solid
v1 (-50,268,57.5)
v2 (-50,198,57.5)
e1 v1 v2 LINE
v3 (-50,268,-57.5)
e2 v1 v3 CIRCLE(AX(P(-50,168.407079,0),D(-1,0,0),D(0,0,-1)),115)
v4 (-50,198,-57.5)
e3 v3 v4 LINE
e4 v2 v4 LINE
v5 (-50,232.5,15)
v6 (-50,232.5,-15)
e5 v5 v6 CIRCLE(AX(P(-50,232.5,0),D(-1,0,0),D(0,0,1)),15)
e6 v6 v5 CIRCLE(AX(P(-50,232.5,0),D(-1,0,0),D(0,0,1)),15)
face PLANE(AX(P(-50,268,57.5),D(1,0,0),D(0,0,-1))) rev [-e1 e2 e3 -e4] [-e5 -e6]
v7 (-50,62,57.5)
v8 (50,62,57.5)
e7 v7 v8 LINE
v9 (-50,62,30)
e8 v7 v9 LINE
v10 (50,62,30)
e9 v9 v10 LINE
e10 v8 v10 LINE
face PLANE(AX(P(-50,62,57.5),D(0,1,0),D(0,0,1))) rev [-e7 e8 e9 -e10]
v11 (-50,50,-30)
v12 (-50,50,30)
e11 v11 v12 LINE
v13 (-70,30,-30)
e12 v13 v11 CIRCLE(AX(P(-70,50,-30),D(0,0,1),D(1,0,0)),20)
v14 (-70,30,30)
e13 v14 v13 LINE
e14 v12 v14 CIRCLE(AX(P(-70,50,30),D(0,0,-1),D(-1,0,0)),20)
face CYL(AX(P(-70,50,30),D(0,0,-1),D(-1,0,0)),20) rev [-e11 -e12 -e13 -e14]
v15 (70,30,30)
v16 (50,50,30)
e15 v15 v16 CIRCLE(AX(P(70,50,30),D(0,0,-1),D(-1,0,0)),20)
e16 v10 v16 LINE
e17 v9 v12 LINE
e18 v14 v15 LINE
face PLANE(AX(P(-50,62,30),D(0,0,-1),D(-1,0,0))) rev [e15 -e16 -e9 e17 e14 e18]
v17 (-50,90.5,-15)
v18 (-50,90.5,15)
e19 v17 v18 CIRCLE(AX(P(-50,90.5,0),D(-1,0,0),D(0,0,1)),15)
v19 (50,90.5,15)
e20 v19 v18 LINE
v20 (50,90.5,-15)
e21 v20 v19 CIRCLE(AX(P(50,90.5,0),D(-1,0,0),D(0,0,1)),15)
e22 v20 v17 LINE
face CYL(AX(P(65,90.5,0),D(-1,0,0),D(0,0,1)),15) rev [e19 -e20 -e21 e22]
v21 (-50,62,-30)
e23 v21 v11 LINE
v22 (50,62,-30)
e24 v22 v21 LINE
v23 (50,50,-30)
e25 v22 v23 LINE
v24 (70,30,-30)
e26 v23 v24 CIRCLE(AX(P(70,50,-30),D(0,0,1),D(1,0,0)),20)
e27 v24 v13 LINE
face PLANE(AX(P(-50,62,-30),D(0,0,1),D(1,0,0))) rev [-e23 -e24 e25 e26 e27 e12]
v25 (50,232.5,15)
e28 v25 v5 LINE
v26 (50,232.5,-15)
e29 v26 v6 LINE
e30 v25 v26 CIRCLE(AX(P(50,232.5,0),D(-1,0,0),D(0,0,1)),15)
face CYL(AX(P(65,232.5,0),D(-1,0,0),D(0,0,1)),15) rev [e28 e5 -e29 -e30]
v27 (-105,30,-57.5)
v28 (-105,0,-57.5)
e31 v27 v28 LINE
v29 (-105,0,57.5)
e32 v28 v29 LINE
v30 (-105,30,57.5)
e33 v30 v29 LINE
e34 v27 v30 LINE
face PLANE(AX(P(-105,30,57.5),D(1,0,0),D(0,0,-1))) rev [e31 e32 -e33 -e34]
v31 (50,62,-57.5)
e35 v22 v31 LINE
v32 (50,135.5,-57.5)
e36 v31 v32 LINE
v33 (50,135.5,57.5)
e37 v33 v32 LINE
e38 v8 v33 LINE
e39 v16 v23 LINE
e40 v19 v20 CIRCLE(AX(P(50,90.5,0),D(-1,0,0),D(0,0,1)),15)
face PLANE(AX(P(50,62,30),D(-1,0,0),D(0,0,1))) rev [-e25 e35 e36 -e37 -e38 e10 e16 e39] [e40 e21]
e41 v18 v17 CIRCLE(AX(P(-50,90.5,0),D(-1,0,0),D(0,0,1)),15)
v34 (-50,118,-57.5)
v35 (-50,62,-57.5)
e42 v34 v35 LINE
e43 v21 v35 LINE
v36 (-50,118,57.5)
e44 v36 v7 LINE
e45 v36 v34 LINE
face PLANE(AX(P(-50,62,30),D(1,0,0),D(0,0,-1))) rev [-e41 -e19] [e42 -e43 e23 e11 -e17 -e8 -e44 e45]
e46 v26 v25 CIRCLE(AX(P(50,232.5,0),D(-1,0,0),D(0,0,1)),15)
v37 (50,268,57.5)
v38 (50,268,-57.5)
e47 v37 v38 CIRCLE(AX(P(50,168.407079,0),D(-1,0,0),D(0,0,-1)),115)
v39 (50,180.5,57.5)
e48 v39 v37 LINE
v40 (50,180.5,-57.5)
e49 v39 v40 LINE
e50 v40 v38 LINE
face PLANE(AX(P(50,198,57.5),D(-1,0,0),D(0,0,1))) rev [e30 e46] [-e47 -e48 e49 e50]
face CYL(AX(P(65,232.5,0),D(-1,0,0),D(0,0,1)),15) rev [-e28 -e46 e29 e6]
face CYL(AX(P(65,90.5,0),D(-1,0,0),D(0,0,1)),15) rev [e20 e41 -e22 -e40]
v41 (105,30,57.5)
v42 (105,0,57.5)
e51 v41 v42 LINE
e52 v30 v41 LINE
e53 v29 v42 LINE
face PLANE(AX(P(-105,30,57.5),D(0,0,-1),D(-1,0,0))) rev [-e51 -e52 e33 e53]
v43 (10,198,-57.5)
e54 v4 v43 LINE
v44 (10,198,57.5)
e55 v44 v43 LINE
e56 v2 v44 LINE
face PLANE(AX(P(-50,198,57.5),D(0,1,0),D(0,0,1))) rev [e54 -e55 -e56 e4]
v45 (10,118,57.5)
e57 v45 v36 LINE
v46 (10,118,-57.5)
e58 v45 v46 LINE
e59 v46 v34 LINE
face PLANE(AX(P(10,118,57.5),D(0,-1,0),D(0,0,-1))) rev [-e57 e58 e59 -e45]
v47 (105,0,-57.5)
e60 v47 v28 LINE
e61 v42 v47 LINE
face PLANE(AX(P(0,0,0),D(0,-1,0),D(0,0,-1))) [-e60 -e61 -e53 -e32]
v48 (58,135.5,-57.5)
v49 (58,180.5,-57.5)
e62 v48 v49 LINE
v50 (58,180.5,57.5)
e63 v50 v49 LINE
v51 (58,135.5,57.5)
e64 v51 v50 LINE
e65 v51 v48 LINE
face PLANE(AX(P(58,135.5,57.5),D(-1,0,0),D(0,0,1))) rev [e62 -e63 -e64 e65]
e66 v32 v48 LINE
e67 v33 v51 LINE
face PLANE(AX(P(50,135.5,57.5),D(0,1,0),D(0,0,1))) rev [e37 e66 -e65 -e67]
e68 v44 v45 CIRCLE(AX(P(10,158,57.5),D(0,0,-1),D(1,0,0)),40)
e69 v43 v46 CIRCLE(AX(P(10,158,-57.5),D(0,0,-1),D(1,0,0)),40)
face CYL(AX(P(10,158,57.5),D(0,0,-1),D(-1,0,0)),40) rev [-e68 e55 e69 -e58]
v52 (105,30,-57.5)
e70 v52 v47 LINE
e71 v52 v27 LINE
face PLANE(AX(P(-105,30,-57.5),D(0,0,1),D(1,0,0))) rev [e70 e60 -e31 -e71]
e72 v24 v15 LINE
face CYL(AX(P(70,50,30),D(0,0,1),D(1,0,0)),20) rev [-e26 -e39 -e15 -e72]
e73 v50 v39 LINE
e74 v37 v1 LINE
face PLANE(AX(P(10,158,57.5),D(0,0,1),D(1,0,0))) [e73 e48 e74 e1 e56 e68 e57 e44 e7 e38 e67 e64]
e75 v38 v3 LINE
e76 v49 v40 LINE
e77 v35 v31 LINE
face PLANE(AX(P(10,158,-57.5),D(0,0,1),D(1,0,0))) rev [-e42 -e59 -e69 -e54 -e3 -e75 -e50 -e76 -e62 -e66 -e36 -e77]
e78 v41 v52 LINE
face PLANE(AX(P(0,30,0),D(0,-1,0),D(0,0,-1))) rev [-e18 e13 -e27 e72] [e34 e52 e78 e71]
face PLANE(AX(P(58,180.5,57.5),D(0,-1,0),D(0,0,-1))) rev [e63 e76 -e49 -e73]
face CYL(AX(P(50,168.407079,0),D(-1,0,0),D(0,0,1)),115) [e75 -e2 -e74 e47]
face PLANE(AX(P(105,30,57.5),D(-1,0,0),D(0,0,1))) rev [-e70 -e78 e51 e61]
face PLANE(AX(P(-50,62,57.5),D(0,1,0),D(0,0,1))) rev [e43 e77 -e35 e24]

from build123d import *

# Parameters (mm, degrees)
BASE_PLATE_SKETCH_W         = 210
BASE_PLATE_SKETCH_H         = 115
BASE_PLATE_210X115X30_DEPTH = 30
PEDESTAL_SKETCH_W           = 100
PEDESTAL_SKETCH_H           = 60
PEDESTAL_100X60X32_DEPTH    = 32
PEDESTAL_FILLET_R20_R       = 20
CLAMP_BLOCK_DEPTH           = 57.5
CROSS_HOLES_SKETCH_R        = 15
CROSS_HOLES_2X_30_DEPTH     = 115
CLAMP_BAND_DEPTH            = 100


with BuildPart() as part:
    # Base Plate Sketch → Base Plate 210x115x30 (new body)
    with BuildSketch(Plane(origin=(0, 0, 0), x_dir=(1, 0, 0), z_dir=(0, 1, 0))):
        Rectangle(BASE_PLATE_SKETCH_W, BASE_PLATE_SKETCH_H)
    extrude(amount=BASE_PLATE_210X115X30_DEPTH)

    # Pedestal Sketch → Pedestal 100x60x32 (add)
    with BuildSketch(Plane(origin=(0, 30, 0), x_dir=(1, 0, 0), z_dir=(0, 1, 0))):
        Rectangle(PEDESTAL_SKETCH_W, PEDESTAL_SKETCH_H)
    extrude(amount=PEDESTAL_100X60X32_DEPTH)

    # Pedestal Fillet R20
    pedestal_fillet_r20_edges = [part.edges().sort_by_distance(p)[0] for p in [
        (50, 30, 0),
        (-50, 30, 0),
    ]]
    fillet(pedestal_fillet_r20_edges, radius=PEDESTAL_FILLET_R20_R)

    # Clamp Block Profile Sketch → Clamp Block (add, symmetric)
    with BuildSketch(Plane.XY):
        with BuildLine():
            Line((50, 62), (50, 118))
            Line((50, 118), (50, 135.5))
            Line((50, 135.5), (58, 135.5))
            Line((58, 135.5), (58, 180.5))
            Line((58, 180.5), (50, 180.5))
            Line((50, 180.5), (50, 198))
            Line((50, 198), (50, 268))
            Line((50, 268), (-50, 268))
            Line((-50, 268), (-50, 198))
            Line((-50, 198), (10, 198))
            ThreePointArc((10, 198), (50, 158), (10, 118))
            Line((10, 118), (-50, 118))
            Line((-50, 118), (-50, 62))
            Line((-50, 62), (50, 62))
        make_face()
    extrude(amount=CLAMP_BLOCK_DEPTH, both=True)

    # Cross Holes Sketch → Cross Holes 2xØ30 (cut)
    with BuildSketch(Plane.ZY.offset(50)):
        with Locations((0, 90.5)):
            Circle(CROSS_HOLES_SKETCH_R)
        with Locations((0, 232.5)):
            Circle(CROSS_HOLES_SKETCH_R)
    extrude(amount=-CROSS_HOLES_2X_30_DEPTH, mode=Mode.SUBTRACT)

    # Clamp Band Sketch → Clamp Band (add)
    with BuildSketch(Plane.ZY.offset(50)):
        with BuildLine():
            Line((-57.5, 268), (57.5, 268))
            ThreePointArc((57.5, 268), (0, 283.407078565), (-57.5, 268))
        make_face()
    extrude(amount=-CLAMP_BAND_DEPTH)


solid = part.part
